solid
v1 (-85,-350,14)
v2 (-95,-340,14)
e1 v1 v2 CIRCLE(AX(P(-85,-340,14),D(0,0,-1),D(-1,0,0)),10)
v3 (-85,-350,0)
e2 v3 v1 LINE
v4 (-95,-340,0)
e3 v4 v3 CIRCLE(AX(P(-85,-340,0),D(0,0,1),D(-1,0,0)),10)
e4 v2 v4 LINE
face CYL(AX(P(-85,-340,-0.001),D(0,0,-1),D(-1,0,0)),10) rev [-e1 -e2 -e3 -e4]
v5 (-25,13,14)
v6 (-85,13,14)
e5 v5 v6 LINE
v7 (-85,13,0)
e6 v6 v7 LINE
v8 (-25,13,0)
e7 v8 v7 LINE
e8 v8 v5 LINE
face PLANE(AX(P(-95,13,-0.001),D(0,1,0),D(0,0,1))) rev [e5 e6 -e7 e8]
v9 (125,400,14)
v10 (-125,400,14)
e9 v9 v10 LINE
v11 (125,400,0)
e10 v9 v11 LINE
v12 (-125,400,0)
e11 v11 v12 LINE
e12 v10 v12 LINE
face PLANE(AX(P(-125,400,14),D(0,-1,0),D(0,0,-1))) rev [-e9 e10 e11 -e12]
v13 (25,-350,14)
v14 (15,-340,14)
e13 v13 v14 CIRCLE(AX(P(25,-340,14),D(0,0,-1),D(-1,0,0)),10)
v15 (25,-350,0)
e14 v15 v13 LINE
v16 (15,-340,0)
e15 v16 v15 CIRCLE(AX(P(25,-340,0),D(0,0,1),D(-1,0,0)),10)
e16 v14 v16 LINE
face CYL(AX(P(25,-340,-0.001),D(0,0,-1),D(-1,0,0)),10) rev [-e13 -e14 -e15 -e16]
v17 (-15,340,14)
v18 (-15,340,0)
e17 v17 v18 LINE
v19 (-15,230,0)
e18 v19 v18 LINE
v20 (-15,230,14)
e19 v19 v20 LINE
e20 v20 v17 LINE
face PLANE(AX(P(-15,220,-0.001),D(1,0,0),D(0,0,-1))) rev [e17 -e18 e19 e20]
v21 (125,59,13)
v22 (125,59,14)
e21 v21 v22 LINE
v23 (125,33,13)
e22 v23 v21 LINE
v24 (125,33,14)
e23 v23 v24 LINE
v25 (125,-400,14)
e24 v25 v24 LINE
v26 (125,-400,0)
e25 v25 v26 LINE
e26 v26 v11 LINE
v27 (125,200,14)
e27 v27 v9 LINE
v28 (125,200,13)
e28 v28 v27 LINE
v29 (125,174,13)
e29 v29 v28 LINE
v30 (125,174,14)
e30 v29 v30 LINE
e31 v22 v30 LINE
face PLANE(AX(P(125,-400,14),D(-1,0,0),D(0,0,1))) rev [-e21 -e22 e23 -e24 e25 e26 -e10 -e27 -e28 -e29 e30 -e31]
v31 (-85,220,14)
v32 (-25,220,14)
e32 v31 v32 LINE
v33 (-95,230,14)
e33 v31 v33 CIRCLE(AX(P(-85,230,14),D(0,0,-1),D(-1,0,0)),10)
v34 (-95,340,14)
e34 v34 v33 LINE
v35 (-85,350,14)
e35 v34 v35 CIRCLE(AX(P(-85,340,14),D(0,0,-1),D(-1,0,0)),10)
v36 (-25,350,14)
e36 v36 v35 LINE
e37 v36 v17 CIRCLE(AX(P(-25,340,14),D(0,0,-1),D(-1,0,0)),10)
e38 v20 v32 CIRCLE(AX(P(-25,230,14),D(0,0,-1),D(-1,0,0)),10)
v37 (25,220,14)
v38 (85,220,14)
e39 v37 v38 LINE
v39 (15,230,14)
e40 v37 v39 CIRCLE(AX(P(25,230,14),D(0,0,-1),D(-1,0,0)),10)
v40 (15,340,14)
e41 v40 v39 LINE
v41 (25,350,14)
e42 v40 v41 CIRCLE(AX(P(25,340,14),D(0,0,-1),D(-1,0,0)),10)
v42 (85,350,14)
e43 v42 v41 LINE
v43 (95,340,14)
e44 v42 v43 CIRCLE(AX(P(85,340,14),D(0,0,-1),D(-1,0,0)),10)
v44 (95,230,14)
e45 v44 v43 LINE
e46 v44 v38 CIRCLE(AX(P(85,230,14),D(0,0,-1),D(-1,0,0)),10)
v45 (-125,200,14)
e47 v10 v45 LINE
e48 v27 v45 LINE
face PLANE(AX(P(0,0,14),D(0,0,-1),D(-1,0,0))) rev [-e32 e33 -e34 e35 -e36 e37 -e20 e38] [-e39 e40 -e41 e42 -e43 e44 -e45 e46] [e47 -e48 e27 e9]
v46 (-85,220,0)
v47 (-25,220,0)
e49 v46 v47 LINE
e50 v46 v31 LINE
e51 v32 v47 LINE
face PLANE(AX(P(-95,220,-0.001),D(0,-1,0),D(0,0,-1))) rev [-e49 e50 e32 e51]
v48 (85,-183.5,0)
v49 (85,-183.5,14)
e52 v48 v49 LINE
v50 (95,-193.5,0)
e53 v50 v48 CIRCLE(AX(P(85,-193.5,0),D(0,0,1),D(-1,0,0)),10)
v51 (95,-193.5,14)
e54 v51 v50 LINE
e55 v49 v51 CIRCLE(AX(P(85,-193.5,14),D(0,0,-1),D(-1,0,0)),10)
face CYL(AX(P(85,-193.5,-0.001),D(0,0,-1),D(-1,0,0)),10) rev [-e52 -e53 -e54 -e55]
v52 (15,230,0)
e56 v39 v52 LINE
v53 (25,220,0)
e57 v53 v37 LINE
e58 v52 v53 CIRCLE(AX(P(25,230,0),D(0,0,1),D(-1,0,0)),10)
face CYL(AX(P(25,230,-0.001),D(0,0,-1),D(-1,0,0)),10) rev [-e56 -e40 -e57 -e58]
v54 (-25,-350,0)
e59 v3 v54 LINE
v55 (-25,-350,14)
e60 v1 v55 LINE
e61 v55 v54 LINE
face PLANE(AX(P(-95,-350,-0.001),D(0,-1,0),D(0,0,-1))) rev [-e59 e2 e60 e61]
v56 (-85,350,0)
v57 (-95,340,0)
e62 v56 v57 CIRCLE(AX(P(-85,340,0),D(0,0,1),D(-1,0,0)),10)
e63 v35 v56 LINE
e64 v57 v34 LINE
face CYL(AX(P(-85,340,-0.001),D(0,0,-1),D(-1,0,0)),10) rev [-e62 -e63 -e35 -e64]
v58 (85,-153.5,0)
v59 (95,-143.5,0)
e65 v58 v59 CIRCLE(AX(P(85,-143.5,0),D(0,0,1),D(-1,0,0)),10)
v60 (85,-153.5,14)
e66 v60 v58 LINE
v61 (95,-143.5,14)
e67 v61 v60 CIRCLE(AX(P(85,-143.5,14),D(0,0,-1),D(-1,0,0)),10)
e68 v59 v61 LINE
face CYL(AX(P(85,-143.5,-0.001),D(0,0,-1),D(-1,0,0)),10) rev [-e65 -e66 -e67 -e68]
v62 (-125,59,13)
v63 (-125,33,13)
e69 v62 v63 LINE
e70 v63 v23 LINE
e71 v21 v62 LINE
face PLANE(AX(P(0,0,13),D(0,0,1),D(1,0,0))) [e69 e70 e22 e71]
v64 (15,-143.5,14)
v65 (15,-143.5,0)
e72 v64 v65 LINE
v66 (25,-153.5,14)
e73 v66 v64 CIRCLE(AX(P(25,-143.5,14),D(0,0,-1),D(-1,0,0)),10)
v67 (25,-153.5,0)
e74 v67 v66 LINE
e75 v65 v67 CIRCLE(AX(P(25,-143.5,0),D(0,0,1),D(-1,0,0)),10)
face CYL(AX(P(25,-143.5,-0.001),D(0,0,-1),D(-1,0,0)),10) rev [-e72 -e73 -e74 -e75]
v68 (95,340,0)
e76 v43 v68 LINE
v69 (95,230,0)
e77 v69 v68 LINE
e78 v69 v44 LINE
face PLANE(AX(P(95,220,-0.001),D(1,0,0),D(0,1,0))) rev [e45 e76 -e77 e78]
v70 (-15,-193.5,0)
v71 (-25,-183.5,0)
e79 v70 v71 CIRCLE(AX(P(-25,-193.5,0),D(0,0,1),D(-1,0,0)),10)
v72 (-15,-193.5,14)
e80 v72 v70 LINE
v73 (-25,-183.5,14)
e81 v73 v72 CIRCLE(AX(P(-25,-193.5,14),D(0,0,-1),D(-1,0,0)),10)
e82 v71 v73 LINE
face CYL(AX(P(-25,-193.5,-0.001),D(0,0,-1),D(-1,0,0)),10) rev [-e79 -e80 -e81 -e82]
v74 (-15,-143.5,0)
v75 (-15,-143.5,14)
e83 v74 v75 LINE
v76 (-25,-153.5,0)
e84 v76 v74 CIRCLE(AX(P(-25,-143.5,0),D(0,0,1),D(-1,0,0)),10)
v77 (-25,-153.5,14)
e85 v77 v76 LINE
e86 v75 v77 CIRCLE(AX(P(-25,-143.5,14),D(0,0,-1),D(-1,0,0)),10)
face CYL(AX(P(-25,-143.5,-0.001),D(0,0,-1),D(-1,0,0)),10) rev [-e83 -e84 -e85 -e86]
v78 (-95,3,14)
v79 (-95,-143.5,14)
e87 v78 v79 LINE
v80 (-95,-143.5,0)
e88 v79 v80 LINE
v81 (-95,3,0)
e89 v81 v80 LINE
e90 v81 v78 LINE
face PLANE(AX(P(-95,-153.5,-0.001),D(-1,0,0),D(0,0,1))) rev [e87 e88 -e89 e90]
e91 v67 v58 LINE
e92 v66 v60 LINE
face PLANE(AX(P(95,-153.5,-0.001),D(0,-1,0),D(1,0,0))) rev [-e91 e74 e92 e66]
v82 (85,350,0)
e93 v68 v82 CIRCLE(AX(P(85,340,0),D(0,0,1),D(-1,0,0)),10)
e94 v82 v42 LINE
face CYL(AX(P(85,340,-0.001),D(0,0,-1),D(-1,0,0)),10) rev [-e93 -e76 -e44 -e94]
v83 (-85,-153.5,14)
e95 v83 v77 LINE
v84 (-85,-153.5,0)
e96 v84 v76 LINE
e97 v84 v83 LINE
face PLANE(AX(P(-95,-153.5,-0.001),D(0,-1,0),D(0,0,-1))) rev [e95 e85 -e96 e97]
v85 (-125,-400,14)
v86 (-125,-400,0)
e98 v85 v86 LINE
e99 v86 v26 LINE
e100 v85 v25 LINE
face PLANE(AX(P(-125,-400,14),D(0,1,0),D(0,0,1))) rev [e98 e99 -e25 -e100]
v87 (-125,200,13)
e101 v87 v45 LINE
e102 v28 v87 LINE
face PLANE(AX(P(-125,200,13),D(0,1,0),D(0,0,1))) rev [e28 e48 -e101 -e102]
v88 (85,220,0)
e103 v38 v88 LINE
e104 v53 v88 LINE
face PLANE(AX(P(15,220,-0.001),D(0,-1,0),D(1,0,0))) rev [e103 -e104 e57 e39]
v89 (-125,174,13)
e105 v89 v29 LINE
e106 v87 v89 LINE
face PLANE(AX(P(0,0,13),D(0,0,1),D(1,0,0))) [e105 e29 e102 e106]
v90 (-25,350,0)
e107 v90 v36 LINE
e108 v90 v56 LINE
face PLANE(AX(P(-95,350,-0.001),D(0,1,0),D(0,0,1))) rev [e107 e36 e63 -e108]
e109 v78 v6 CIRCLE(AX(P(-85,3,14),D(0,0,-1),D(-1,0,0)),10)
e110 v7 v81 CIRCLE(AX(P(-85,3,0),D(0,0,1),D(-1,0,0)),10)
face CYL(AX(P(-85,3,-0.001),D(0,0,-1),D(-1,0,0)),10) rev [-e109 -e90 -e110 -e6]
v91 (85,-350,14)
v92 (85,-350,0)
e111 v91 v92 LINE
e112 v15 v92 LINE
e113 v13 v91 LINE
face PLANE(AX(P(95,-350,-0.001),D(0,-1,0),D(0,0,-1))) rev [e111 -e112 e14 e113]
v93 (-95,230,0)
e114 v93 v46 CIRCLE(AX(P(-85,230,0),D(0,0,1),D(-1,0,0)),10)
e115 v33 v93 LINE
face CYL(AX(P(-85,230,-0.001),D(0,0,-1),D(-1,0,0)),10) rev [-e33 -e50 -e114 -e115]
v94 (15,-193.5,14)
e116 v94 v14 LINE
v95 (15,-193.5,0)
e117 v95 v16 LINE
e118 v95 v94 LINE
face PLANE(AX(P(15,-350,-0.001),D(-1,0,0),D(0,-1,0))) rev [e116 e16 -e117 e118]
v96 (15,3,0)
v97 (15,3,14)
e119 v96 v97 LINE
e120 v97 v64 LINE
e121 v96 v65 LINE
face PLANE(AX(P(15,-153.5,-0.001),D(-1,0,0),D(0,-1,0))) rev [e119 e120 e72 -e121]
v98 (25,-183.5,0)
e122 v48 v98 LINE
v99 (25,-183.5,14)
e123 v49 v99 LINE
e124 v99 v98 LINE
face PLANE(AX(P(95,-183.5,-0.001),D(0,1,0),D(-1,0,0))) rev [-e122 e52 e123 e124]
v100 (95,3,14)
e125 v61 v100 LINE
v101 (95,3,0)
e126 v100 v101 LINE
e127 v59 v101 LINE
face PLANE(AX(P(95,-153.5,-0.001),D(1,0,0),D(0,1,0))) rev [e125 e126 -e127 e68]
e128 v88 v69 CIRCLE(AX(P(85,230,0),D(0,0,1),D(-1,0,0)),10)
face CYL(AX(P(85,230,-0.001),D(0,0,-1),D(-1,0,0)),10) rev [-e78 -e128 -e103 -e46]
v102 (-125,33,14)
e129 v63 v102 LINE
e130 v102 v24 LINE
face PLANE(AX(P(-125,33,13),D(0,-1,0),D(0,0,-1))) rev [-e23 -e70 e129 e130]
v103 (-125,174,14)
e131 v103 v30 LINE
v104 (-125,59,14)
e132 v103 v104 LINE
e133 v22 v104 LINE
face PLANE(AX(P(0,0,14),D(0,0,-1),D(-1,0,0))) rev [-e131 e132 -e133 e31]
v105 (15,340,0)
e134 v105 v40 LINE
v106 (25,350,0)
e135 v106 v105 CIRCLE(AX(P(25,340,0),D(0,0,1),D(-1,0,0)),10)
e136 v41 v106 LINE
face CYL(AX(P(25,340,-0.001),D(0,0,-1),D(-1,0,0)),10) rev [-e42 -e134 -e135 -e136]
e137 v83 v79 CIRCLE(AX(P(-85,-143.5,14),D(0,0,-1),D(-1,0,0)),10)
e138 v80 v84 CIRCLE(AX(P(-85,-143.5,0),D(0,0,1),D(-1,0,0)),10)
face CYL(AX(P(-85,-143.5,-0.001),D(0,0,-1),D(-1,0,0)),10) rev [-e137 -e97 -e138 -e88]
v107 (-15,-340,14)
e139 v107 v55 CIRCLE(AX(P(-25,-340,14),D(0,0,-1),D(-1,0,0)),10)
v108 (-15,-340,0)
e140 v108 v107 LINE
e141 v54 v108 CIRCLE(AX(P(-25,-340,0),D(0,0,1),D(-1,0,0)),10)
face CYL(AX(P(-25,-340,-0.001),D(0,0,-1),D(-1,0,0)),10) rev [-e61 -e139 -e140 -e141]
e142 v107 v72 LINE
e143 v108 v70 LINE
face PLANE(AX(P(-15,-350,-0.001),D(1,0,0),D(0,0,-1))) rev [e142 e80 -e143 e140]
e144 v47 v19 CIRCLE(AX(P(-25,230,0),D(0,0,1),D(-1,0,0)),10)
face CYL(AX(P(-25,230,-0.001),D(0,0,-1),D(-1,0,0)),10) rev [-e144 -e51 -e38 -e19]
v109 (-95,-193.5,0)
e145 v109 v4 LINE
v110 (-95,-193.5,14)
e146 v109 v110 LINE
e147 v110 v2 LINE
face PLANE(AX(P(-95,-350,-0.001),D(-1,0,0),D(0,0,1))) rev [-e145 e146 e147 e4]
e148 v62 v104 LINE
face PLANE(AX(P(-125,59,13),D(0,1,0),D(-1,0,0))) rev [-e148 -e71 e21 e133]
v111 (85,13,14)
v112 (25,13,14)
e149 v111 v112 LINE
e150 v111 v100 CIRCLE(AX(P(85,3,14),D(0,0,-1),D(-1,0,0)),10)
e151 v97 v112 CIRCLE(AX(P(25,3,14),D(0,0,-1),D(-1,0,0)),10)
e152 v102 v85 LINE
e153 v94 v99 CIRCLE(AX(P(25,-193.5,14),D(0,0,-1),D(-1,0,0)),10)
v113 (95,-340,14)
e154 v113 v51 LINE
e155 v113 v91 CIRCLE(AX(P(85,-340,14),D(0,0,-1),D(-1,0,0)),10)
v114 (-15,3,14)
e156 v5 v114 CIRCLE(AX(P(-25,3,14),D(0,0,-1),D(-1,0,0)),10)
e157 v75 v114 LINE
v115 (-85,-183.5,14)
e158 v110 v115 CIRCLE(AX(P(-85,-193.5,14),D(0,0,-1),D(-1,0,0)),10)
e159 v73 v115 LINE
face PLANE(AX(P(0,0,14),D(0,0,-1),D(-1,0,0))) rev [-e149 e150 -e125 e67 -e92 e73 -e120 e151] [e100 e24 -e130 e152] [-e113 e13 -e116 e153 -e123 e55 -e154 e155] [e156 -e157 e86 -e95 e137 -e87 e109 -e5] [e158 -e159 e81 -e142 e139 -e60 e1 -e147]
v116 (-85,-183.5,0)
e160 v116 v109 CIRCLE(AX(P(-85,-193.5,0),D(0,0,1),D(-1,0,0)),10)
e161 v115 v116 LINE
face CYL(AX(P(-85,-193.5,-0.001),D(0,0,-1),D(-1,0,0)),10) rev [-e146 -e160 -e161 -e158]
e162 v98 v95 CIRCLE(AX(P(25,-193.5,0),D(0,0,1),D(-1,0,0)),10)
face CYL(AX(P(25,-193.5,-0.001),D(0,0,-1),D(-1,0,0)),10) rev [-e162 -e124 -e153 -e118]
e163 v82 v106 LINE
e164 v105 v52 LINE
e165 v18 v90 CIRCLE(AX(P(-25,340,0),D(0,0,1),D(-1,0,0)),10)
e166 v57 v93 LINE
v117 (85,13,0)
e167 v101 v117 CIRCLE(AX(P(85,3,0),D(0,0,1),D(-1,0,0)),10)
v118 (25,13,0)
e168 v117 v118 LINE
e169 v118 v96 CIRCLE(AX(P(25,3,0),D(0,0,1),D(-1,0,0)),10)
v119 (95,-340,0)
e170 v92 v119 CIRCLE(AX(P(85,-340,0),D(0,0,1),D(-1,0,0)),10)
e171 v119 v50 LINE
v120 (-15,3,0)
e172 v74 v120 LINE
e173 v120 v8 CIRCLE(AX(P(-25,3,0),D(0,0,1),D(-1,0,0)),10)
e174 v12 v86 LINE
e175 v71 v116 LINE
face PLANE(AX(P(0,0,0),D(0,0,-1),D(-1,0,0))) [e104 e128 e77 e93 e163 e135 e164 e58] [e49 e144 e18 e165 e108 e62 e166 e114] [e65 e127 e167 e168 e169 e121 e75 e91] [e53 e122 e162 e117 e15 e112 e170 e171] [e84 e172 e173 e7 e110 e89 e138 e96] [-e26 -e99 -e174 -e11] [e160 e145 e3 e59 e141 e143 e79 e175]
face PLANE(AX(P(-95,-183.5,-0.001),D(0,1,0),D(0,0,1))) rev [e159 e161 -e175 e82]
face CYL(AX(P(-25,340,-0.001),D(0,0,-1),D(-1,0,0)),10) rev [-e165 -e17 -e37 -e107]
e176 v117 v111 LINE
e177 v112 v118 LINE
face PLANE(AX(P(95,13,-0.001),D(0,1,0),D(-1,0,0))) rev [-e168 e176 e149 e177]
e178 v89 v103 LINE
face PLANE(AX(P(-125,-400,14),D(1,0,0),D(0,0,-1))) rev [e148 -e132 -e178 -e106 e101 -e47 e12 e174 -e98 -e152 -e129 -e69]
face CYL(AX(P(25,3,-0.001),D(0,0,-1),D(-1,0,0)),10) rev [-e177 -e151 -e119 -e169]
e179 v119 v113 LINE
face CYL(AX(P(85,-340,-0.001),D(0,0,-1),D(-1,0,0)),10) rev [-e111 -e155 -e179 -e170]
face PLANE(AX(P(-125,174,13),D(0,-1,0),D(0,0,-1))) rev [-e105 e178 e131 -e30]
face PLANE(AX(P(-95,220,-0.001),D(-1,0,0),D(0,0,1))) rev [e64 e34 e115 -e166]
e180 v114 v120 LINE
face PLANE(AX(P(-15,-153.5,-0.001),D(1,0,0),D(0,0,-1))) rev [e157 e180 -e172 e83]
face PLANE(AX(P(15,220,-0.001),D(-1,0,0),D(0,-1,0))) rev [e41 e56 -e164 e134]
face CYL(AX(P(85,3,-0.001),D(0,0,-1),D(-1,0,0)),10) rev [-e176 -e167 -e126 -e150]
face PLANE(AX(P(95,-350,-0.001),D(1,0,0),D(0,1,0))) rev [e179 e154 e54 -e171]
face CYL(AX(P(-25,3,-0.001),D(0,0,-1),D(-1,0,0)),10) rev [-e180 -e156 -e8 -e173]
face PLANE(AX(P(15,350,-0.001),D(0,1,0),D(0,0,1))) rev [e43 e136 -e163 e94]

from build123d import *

# Parameters (mm, degrees)
SKETCH_1_W          = 250
SKETCH_1_H          = 800
EXTRUDE_1_DEPTH     = 14
SKETCH_2_W          = 250
SKETCH_2_H          = 26
CUT_EXTRUDE_1_DEPTH = 1
CUT_EXTRUDE_2_REACH = 421.31
SKETCH_3_W          = 80
SKETCH_3_H          = 166.5
SKETCH_3_H_2        = 130
FILLET_1_R          = 10


with BuildPart() as part:
    # 草图1 → 凸台-拉伸1 (new body)
    with BuildSketch(Plane.XY):
        Rectangle(SKETCH_1_W, SKETCH_1_H)
    extrude(amount=EXTRUDE_1_DEPTH)

    # 草图2 → 切除-拉伸1 (cut)
    with BuildSketch(Plane.XY.offset(14)):
        with Locations((0, 187)):
            Rectangle(SKETCH_2_W, SKETCH_2_H)
        with Locations((0, 46)):
            Rectangle(SKETCH_2_W, SKETCH_2_H)
    extrude(amount=-CUT_EXTRUDE_1_DEPTH, mode=Mode.SUBTRACT)

    # 草图3 → 切除-拉伸2 (cut, up to next)
    with BuildSketch(Plane.XY.offset(14), mode=Mode.PRIVATE) as cut_extrude_2_sk1:
        with Locations((-55, -70.25)):
            Rectangle(SKETCH_3_W, SKETCH_3_H)
    cut_extrude_2_tool1 = extrude(cut_extrude_2_sk1.sketch, amount=-CUT_EXTRUDE_2_REACH, mode=Mode.PRIVATE) & part.part
    # 草图3 → 切除-拉伸2 (cut, up to next)
    with BuildSketch(Plane.XY.offset(14), mode=Mode.PRIVATE) as cut_extrude_2_sk2:
        with Locations((-55, -266.75)):
            Rectangle(SKETCH_3_W, SKETCH_3_H)
    cut_extrude_2_tool2 = extrude(cut_extrude_2_sk2.sketch, amount=-CUT_EXTRUDE_2_REACH, mode=Mode.PRIVATE) & part.part
    # 草图3 → 切除-拉伸2 (cut, up to next)
    with BuildSketch(Plane.XY.offset(14), mode=Mode.PRIVATE) as cut_extrude_2_sk3:
        with Locations((55, -266.75)):
            Rectangle(SKETCH_3_W, SKETCH_3_H)
    cut_extrude_2_tool3 = extrude(cut_extrude_2_sk3.sketch, amount=-CUT_EXTRUDE_2_REACH, mode=Mode.PRIVATE) & part.part
    # 草图3 → 切除-拉伸2 (cut, up to next)
    with BuildSketch(Plane.XY.offset(14), mode=Mode.PRIVATE) as cut_extrude_2_sk4:
        with Locations((55, -70.25)):
            Rectangle(SKETCH_3_W, SKETCH_3_H)
    cut_extrude_2_tool4 = extrude(cut_extrude_2_sk4.sketch, amount=-CUT_EXTRUDE_2_REACH, mode=Mode.PRIVATE) & part.part
    # 草图3 → 切除-拉伸2 (cut, up to next)
    with BuildSketch(Plane.XY.offset(14), mode=Mode.PRIVATE) as cut_extrude_2_sk5:
        with Locations((-55, 285)):
            Rectangle(SKETCH_3_W, SKETCH_3_H_2)
    cut_extrude_2_tool5 = extrude(cut_extrude_2_sk5.sketch, amount=-CUT_EXTRUDE_2_REACH, mode=Mode.PRIVATE) & part.part
    # 草图3 → 切除-拉伸2 (cut, up to next)
    with BuildSketch(Plane.XY.offset(14), mode=Mode.PRIVATE) as cut_extrude_2_sk6:
        with Locations((55, 285)):
            Rectangle(SKETCH_3_W, SKETCH_3_H_2)
    cut_extrude_2_tool6 = extrude(cut_extrude_2_sk6.sketch, amount=-CUT_EXTRUDE_2_REACH, mode=Mode.PRIVATE) & part.part
    add(cut_extrude_2_tool1.solids().sort_by_distance((-55, -70.25, 14))[0], mode=Mode.SUBTRACT)
    add(cut_extrude_2_tool2.solids().sort_by_distance((-55, -266.75, 14))[0], mode=Mode.SUBTRACT)
    add(cut_extrude_2_tool3.solids().sort_by_distance((55, -266.75, 14))[0], mode=Mode.SUBTRACT)
    add(cut_extrude_2_tool4.solids().sort_by_distance((55, -70.25, 14))[0], mode=Mode.SUBTRACT)
    add(cut_extrude_2_tool5.solids().sort_by_distance((-55, 285, 14))[0], mode=Mode.SUBTRACT)
    add(cut_extrude_2_tool6.solids().sort_by_distance((55, 285, 14))[0], mode=Mode.SUBTRACT)

    # 圆角1
    fillet_1_edges = [part.edges().sort_by_distance(p)[0] for p in [
        (-15, -183.5, 7),
        (-15, -350, 7),
        (-95, -350, 7),
        (-95, -183.5, 7),
        (95, -183.5, 7),
        (95, -350, 7),
        (15, -350, 7),
        (15, -183.5, 7),
        (95, 13, 7),
        (95, -153.5, 7),
        (15, -153.5, 7),
        (15, 13, 7),
        (-15, 350, 7),
        (-15, 220, 7),
        (-95, 220, 7),
        (-95, 350, 7),
        (95, 350, 7),
        (95, 220, 7),
        (15, 220, 7),
        (15, 350, 7),
        (-15, 13, 7),
        (-15, -153.5, 7),
        (-95, -153.5, 7),
        (-95, 13, 7),
    ]]
    fillet(fillet_1_edges, radius=FILLET_1_R)


solid = part.part
